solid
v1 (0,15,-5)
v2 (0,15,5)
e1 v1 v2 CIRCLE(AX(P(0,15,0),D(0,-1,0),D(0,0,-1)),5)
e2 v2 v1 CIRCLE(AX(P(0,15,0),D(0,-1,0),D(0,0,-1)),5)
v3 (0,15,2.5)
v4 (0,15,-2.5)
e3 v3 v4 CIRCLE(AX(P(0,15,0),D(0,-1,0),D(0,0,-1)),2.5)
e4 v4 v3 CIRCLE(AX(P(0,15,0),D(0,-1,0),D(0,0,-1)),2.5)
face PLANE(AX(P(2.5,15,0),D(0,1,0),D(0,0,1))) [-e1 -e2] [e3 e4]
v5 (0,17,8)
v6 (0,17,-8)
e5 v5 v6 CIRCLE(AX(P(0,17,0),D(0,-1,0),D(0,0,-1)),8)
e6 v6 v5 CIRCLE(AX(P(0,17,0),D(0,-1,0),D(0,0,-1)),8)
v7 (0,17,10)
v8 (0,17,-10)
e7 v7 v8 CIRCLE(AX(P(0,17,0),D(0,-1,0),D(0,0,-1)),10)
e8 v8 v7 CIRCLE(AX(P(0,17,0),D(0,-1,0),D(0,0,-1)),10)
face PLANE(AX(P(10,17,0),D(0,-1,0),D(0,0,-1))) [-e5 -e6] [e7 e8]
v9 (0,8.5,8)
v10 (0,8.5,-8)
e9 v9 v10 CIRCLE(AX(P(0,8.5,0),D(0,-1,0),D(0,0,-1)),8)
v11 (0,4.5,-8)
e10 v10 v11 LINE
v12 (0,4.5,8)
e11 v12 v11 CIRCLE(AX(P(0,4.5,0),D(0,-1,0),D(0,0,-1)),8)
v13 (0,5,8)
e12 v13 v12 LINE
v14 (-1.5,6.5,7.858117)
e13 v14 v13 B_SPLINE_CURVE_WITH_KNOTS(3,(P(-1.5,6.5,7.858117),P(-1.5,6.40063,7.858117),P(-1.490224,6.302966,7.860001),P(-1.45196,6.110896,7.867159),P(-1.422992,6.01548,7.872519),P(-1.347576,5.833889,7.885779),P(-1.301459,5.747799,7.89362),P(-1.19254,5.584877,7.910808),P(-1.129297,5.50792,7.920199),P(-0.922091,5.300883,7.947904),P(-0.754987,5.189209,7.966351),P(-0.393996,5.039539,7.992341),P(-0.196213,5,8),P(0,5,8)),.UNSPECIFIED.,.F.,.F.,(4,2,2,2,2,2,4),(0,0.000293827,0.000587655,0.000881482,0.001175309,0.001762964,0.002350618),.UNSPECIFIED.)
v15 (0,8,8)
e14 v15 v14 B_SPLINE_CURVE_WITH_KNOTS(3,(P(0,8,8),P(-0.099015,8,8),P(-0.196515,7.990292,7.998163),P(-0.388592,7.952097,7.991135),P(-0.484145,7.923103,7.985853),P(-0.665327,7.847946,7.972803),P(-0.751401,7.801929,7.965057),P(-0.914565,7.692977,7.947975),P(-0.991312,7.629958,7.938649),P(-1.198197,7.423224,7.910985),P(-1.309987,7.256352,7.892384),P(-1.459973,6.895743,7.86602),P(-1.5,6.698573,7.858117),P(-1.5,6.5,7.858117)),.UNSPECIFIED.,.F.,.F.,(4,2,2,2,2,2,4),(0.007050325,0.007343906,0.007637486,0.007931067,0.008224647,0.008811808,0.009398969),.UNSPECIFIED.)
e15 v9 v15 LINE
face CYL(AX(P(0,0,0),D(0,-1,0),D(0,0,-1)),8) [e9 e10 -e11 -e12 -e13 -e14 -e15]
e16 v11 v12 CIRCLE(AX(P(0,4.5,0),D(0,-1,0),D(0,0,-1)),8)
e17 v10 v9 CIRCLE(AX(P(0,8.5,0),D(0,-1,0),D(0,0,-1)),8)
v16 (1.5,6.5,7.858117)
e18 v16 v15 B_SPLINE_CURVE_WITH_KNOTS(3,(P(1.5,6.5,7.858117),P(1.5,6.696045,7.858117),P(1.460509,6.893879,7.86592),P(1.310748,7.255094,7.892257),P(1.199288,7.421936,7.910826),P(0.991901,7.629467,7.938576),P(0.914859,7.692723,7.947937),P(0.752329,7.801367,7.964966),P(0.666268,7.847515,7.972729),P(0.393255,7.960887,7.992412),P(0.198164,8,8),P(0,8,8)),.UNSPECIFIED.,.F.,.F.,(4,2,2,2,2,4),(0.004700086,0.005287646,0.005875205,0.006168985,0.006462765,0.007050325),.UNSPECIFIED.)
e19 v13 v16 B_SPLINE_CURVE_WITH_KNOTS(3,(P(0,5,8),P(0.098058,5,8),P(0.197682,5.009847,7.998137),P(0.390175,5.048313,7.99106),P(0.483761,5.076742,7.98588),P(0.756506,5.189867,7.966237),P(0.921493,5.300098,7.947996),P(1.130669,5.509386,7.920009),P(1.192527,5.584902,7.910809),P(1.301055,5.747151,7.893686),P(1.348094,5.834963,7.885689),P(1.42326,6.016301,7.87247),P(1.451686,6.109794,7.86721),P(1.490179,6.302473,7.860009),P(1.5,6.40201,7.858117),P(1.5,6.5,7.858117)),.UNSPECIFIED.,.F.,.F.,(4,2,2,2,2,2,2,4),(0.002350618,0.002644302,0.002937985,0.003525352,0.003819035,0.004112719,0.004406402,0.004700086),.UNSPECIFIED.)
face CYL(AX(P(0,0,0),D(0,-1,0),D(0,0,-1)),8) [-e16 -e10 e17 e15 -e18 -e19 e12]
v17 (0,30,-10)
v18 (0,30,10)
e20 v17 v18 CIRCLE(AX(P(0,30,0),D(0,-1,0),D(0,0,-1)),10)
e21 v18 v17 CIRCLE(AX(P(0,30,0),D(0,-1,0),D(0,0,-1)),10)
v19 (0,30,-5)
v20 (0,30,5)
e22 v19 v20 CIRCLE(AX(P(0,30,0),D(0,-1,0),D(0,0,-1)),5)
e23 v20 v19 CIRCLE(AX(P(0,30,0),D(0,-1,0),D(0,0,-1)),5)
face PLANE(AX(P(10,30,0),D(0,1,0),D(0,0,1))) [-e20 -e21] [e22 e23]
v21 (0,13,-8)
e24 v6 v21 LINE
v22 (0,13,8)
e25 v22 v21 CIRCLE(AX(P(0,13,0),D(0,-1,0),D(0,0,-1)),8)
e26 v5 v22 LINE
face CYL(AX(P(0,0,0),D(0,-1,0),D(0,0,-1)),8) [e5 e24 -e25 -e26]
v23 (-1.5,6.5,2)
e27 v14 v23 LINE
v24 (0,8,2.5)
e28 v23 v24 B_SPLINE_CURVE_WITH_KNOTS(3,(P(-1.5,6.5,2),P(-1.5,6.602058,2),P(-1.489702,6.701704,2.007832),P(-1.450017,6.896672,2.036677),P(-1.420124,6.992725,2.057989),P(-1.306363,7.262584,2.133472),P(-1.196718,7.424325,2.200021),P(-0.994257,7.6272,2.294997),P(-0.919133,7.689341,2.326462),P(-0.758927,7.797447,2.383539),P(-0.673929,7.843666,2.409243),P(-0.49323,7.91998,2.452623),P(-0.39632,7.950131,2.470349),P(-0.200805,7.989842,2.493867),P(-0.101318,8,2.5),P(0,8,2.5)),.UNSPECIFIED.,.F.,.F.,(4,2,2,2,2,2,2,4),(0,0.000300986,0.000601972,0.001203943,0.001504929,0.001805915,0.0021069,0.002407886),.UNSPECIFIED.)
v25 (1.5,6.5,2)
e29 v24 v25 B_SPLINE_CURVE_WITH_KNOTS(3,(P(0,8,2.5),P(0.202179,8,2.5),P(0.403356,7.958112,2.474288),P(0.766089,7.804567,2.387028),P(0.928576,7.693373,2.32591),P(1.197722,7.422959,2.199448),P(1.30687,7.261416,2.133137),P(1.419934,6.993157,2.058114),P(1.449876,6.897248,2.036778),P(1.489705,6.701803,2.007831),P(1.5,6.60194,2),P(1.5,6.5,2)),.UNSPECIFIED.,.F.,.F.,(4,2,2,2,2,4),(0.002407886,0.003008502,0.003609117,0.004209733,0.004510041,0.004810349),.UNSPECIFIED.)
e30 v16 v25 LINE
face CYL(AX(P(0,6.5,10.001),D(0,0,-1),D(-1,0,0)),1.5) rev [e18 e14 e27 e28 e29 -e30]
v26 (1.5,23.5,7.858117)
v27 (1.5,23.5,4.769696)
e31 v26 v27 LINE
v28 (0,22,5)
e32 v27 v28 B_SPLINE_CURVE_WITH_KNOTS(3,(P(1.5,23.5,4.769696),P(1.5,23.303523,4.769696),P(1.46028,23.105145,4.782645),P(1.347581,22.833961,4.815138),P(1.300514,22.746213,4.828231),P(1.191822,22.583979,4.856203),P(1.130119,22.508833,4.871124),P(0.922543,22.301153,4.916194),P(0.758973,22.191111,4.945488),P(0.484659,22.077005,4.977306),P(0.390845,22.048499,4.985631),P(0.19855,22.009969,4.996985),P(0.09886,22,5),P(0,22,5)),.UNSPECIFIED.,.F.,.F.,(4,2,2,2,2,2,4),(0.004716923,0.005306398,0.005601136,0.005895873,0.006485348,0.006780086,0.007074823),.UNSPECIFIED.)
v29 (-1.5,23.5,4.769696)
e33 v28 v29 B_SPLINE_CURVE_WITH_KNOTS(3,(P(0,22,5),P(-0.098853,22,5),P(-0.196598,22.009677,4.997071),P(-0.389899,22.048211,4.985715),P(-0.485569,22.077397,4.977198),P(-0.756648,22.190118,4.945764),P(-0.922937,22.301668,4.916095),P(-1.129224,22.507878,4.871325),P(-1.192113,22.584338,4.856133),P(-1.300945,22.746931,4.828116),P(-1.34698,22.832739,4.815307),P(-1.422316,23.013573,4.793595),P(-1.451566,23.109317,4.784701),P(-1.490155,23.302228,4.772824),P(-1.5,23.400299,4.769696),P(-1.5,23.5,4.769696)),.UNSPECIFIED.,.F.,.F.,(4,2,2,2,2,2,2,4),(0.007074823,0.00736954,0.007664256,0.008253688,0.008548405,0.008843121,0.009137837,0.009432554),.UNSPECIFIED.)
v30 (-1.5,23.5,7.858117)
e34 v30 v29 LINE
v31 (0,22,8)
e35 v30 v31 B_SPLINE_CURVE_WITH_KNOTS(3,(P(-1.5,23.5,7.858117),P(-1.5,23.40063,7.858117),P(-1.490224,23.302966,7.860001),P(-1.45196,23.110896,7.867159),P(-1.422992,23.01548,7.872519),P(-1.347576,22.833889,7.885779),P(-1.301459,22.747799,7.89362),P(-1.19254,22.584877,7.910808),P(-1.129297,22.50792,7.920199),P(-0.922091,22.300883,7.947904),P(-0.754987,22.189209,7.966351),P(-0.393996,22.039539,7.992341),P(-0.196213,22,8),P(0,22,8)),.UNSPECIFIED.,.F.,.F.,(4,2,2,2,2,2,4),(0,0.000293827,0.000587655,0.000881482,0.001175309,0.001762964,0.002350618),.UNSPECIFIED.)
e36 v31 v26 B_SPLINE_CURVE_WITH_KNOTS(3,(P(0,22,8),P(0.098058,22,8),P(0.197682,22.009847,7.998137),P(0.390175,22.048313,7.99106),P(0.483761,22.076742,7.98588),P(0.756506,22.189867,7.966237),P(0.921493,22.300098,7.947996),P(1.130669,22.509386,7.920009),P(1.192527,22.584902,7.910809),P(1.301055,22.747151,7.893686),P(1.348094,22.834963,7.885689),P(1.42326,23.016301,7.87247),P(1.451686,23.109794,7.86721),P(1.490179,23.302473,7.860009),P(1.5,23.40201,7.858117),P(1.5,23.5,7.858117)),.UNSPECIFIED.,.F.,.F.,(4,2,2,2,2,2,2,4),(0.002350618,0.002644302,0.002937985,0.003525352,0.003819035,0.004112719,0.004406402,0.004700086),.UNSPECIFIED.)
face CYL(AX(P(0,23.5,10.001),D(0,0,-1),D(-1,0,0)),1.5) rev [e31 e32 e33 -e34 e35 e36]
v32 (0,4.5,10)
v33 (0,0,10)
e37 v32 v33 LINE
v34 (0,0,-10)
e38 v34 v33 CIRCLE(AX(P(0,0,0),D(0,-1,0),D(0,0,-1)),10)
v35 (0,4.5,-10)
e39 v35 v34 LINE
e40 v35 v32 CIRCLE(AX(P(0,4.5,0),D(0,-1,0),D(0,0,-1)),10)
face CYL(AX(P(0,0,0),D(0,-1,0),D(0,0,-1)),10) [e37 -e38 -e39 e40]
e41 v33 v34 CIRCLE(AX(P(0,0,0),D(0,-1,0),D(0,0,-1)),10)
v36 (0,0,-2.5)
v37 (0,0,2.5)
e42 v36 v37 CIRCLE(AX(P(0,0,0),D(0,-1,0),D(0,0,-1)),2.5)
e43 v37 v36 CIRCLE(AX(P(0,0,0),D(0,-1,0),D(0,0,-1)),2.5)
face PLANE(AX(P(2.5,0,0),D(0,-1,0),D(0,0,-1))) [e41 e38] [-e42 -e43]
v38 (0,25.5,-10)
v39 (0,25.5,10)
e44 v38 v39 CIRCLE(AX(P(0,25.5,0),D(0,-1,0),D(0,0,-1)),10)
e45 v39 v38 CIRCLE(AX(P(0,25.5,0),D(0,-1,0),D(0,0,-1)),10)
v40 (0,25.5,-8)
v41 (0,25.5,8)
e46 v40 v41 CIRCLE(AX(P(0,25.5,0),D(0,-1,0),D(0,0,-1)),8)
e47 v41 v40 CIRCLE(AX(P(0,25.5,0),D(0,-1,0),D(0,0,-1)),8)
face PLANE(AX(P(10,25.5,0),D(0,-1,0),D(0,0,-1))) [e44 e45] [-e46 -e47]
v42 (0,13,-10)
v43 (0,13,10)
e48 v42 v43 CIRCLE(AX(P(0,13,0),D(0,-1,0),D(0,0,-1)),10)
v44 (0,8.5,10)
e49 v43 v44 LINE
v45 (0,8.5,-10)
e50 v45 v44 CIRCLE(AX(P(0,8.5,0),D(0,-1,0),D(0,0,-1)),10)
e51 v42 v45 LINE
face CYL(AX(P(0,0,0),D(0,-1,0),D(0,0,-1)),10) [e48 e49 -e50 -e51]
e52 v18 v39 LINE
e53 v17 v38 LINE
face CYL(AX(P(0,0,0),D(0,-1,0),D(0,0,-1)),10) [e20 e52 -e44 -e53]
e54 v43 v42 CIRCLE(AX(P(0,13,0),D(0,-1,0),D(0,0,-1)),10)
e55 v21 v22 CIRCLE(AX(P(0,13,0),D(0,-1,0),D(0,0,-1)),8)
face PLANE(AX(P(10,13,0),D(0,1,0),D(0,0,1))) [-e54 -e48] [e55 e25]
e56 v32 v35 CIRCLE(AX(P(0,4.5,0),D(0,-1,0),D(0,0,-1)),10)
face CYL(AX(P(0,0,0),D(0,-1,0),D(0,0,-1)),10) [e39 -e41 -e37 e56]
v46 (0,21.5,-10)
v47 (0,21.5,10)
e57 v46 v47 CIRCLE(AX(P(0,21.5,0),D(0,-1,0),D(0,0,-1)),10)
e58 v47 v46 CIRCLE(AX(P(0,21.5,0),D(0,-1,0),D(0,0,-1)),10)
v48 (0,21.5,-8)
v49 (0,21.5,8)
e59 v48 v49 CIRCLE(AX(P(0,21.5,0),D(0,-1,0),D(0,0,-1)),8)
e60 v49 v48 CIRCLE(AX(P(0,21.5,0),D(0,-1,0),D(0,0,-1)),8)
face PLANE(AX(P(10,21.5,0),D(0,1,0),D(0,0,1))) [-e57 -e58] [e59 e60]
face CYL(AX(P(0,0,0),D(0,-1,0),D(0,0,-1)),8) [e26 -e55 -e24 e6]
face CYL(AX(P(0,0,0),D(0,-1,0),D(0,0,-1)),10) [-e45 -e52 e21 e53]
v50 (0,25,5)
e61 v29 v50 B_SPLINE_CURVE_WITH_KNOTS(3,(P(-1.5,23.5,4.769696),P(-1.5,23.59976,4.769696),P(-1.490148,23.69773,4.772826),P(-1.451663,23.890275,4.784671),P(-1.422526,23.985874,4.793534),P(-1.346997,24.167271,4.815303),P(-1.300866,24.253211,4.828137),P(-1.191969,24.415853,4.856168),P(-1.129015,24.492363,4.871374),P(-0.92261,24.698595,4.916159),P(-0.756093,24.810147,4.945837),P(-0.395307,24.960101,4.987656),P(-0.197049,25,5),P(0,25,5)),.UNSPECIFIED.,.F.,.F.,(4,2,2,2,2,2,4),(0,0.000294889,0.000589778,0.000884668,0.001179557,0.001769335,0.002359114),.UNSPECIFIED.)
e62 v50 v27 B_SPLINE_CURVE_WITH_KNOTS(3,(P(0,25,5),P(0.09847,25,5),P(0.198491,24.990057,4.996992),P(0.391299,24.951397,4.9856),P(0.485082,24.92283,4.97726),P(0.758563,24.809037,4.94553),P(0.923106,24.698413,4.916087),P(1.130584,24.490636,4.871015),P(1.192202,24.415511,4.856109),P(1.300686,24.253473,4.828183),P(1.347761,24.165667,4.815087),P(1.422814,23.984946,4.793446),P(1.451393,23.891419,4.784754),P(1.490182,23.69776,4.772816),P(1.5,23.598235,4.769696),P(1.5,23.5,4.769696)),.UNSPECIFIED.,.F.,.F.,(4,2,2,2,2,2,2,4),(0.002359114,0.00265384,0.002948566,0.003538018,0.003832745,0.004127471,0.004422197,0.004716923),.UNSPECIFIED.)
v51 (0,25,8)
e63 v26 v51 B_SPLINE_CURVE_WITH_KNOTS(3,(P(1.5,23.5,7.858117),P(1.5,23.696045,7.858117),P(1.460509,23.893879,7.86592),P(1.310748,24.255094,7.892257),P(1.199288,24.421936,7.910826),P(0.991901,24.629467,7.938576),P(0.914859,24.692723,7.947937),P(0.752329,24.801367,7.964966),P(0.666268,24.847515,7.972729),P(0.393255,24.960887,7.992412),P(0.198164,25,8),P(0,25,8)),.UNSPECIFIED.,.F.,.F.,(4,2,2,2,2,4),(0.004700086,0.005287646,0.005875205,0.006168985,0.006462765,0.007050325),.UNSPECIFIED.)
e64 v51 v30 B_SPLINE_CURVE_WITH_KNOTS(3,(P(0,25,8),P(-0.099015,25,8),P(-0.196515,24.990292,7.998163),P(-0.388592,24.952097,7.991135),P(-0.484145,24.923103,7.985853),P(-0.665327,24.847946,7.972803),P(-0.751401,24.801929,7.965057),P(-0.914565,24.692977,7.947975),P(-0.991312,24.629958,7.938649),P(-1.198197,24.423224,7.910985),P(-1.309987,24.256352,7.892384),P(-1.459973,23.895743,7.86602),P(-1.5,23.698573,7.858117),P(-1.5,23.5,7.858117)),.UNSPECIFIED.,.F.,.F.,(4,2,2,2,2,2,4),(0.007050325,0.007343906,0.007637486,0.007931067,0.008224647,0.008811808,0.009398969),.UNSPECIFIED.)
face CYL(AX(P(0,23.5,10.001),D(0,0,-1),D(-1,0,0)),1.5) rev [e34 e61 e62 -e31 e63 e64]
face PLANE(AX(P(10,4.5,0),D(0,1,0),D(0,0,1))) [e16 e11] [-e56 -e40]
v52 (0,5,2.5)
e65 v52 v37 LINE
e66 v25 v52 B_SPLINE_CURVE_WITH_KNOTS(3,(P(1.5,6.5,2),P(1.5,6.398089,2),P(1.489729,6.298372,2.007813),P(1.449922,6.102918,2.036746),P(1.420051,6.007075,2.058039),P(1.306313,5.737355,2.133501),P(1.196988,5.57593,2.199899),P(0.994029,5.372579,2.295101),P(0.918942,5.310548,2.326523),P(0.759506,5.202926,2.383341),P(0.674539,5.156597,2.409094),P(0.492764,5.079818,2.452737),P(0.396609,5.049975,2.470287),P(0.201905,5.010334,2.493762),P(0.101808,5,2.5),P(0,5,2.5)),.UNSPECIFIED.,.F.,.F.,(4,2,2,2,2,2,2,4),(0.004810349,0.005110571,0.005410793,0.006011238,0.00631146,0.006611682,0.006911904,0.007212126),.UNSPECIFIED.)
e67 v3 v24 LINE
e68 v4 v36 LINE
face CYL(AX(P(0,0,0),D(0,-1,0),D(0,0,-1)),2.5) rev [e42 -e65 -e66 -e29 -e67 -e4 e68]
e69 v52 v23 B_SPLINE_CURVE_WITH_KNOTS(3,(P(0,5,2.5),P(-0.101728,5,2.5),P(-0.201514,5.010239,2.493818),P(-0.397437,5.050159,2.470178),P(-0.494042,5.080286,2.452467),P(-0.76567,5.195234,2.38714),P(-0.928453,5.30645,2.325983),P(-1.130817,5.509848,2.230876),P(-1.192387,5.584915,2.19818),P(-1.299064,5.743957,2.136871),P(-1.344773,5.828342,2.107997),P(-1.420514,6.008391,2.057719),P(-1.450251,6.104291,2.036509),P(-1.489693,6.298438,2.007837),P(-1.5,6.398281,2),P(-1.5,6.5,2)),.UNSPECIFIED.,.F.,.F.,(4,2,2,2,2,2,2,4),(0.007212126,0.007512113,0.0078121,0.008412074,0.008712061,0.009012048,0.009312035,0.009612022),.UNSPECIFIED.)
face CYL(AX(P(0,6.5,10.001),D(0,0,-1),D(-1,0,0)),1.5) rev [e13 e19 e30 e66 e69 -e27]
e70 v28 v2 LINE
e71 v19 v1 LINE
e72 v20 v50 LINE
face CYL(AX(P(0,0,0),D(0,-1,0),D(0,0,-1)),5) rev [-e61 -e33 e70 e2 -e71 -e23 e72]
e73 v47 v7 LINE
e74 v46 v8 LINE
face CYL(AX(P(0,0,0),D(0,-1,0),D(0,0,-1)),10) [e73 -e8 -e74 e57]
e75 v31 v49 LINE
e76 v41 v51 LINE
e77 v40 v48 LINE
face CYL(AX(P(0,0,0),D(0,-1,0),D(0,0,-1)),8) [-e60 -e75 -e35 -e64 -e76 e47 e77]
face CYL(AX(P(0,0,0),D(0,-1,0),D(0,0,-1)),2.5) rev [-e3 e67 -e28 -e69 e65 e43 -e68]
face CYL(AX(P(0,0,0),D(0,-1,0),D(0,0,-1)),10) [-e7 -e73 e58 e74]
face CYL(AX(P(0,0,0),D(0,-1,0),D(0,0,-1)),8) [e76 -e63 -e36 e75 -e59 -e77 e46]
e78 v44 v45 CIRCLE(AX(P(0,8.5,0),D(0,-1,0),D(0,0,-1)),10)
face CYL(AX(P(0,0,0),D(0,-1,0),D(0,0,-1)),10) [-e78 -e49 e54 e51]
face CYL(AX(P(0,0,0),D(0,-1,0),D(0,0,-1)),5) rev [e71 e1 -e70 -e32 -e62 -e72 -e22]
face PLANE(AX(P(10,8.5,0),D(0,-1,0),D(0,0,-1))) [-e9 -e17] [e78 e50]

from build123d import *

# Parameters (mm, degrees)
CUT_EXTRUDE1_REACH      = 35.166
CUT_EXTRUDE1_END_RADIUS = 8
SKETCH2_R               = 1.5


with BuildPart() as part:
    # Sketch1 → Revolve1 (revolve)
    with BuildSketch(Plane.XY, mode=Mode.PRIVATE) as revolve1_sk:
        Polygon((2.5, 15), (2.5, 0), (10, 0), (10, 4.5), (8, 4.5), (8, 8.5), (10, 8.5), (10, 13), (8, 13), (8, 17), (10, 17), (10, 21.5), (8, 21.5), (8, 25.5), (10, 25.5), (10, 30), (5, 30), (5, 15), align=None)
    revolve(revolve1_sk.sketch.rotate(Axis((0, 0, 0), (0, 1, 0)), 90), axis=Axis((0, 0, 0), (0, 1, 0)))

    # Cut-Extrude1: up to this cylinder (the profile starts inside it)
    cut_extrude1_end = Plane(origin=(0, 15, 0), z_dir=(0, -1, 0)) * Cylinder(CUT_EXTRUDE1_END_RADIUS, 104.332, mode=Mode.PRIVATE)
    # Sketch2 → Cut-Extrude1 (cut, up to the surface)
    with BuildSketch(Plane.XY, mode=Mode.PRIVATE) as cut_extrude1_sk1:
        with Locations(Location((0, 23.5, 0), (0, 0, 180))):
            Circle(SKETCH2_R)
    cut_extrude1_tool1 = extrude(cut_extrude1_sk1.sketch, amount=CUT_EXTRUDE1_REACH, mode=Mode.PRIVATE) & cut_extrude1_end
    add(cut_extrude1_tool1.solids().sort_by_distance((0, 23.5, 0))[0], mode=Mode.SUBTRACT)
    # Sketch2 → Cut-Extrude1 (cut, up to the surface)
    with BuildSketch(Plane.XY, mode=Mode.PRIVATE) as cut_extrude1_sk2:
        with Locations(Location((0, 6.5, 0), (0, 0, 180))):
            Circle(SKETCH2_R)
    cut_extrude1_tool2 = extrude(cut_extrude1_sk2.sketch, amount=CUT_EXTRUDE1_REACH, mode=Mode.PRIVATE) & cut_extrude1_end
    add(cut_extrude1_tool2.solids().sort_by_distance((0, 6.5, 0))[0], mode=Mode.SUBTRACT)


solid = part.part
